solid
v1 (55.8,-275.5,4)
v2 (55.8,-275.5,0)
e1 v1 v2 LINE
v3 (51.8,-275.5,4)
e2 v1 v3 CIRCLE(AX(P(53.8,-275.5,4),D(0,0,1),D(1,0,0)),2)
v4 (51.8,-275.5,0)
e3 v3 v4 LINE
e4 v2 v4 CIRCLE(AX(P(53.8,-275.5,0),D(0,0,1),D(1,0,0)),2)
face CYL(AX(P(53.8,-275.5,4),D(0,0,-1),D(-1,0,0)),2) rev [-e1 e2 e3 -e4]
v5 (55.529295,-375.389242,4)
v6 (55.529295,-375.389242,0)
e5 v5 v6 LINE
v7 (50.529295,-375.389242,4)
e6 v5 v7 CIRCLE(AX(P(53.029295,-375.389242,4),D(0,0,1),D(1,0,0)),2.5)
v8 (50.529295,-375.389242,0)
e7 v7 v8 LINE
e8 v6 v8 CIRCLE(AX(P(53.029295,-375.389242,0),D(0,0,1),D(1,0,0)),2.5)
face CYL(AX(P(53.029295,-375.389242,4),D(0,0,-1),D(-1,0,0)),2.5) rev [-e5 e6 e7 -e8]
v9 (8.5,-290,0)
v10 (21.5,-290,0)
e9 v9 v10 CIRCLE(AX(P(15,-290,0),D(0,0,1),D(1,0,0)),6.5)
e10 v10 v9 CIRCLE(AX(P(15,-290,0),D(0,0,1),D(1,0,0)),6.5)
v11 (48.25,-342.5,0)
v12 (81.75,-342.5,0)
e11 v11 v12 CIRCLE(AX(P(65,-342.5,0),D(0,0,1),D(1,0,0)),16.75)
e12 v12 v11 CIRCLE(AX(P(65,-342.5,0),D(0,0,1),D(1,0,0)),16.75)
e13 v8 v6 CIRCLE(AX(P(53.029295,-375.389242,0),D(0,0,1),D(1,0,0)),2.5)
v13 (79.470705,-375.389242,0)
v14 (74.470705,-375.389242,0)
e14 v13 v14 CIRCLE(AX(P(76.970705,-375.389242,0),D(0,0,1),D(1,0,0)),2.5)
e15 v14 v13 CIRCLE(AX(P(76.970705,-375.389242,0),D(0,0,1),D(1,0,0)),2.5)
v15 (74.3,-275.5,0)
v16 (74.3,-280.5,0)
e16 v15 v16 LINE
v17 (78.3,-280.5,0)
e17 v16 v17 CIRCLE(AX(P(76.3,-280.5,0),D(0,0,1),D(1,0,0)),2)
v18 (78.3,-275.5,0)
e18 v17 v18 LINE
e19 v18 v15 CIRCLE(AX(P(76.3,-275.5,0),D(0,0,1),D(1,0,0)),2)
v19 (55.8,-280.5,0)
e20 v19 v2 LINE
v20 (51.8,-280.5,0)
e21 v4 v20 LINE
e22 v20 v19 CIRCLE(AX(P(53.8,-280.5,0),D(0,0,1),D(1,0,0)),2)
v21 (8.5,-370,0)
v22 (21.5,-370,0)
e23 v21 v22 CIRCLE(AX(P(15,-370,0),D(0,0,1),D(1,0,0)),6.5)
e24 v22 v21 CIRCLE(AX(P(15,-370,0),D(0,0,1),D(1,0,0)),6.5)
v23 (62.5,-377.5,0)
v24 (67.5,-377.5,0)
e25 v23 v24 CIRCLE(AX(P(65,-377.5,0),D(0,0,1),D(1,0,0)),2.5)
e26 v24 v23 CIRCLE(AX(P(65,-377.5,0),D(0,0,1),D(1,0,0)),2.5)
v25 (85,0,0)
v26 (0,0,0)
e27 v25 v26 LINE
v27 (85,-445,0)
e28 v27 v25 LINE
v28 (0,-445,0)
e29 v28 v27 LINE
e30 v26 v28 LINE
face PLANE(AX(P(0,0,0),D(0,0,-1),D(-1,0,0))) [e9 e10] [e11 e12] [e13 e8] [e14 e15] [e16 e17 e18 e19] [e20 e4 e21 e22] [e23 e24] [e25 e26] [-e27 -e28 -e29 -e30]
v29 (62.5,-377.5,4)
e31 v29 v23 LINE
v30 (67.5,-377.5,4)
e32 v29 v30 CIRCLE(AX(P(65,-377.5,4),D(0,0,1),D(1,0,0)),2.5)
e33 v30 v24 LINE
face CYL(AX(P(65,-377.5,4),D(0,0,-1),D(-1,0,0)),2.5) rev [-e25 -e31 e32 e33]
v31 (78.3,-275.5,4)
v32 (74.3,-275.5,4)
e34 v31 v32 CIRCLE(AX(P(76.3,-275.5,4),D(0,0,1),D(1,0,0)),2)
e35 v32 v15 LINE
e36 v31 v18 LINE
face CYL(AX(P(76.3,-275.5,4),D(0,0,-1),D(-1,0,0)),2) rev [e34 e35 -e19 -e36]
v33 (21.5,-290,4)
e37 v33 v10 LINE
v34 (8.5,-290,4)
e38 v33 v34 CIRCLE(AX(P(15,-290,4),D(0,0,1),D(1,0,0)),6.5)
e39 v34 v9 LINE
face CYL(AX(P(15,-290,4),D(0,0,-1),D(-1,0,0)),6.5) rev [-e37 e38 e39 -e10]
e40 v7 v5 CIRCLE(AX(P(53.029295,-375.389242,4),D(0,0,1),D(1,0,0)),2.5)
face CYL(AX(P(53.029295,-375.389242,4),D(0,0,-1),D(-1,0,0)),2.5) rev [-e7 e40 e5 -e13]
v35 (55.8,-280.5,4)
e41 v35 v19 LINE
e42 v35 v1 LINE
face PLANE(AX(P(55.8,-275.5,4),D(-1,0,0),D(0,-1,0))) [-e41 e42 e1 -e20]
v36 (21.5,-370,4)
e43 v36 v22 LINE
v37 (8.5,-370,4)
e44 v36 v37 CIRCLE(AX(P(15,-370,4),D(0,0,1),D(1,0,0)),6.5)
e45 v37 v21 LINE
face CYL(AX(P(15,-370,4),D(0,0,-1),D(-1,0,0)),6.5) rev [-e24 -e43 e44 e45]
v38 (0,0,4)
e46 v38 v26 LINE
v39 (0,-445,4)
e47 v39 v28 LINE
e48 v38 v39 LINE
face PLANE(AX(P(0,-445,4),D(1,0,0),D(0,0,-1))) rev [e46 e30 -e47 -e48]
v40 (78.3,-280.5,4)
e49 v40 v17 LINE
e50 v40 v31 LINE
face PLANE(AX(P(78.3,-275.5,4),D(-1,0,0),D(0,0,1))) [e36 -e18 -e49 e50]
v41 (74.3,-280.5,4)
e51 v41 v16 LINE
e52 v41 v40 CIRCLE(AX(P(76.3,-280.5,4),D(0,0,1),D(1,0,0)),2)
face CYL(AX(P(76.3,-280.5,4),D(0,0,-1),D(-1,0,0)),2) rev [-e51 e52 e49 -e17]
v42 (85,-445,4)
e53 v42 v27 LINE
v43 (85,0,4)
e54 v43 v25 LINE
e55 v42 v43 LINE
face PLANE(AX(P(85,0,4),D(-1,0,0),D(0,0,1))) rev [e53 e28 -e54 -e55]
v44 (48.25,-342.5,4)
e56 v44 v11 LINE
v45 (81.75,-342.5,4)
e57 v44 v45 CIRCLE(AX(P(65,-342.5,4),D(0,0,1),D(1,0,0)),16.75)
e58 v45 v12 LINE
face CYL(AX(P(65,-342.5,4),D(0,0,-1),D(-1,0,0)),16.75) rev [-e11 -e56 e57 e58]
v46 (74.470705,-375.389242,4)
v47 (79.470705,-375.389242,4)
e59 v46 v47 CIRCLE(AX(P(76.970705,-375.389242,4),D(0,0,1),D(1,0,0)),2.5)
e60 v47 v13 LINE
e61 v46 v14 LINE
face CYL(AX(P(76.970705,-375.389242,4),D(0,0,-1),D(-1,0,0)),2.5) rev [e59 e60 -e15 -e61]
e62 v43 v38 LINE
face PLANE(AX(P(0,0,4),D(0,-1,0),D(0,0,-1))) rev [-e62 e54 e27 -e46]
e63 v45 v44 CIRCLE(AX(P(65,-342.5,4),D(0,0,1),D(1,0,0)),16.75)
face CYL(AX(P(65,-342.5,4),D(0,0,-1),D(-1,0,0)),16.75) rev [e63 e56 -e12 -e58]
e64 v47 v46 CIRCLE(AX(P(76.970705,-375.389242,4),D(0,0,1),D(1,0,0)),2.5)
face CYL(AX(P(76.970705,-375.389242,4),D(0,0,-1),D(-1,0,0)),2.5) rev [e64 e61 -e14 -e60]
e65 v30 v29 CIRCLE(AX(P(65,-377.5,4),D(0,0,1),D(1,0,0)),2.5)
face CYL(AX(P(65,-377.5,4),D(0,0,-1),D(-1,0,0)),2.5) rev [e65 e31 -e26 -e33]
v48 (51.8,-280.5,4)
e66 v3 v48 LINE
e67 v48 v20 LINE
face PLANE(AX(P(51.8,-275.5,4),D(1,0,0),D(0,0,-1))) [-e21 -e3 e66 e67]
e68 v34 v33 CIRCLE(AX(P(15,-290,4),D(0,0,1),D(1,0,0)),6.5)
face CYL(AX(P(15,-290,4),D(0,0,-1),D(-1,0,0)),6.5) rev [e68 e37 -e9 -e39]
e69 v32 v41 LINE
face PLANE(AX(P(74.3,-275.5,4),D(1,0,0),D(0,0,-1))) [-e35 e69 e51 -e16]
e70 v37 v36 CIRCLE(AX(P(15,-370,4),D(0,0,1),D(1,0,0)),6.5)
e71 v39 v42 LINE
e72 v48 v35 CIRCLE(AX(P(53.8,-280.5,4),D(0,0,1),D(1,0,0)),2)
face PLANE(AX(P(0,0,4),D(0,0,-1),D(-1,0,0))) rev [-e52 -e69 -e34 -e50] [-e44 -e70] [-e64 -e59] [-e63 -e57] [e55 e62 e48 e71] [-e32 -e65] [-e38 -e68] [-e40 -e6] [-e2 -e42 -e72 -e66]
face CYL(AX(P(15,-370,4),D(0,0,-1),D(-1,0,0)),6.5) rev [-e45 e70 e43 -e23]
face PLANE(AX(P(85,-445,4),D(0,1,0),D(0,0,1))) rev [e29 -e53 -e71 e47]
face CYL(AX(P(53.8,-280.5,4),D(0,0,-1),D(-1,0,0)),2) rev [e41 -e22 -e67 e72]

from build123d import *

# Parameters (mm, degrees)
SKETCH_1_W      = 85
SKETCH_1_H      = 445
SKETCH_1_R      = 6.5
SKETCH_1_R_2    = 2.5
SKETCH_1_R_3    = 16.75
EXTRUDE_2_DEPTH = 4


with BuildPart() as part:
    # 草图1 → 凸台-拉伸2 (new body)
    with BuildSketch(Plane.XY):
        with Locations((42.5, -222.5)):
            Rectangle(SKETCH_1_W, SKETCH_1_H)
        with Locations((15, -370)):
            Circle(SKETCH_1_R, mode=Mode.SUBTRACT)
        with Locations((76.970705016, -375.389241728)):
            Circle(SKETCH_1_R_2, mode=Mode.SUBTRACT)
        with Locations((65, -377.5)):
            Circle(SKETCH_1_R_2, mode=Mode.SUBTRACT)
        with Locations((15, -290)):
            Circle(SKETCH_1_R, mode=Mode.SUBTRACT)
        with Locations((53.029294983, -375.389241728)):
            Circle(SKETCH_1_R_2, mode=Mode.SUBTRACT)
        with Locations((65, -342.5)):
            Circle(SKETCH_1_R_3, mode=Mode.SUBTRACT)
        with BuildLine():
            Line((78.3, -275.5), (78.3, -280.5))
            ThreePointArc((78.3, -280.5), (76.3, -282.5), (74.3, -280.5))
            Line((74.3, -280.5), (74.3, -275.5))
            ThreePointArc((74.3, -275.5), (76.3, -273.5), (78.3, -275.5))
        make_face(mode=Mode.SUBTRACT)
        with BuildLine():
            Line((55.8, -275.5), (55.8, -280.5))
            ThreePointArc((55.8, -280.5), (53.8, -282.5), (51.8, -280.5))
            Line((51.8, -280.5), (51.8, -275.5))
            ThreePointArc((51.8, -275.5), (53.8, -273.5), (55.8, -275.5))
        make_face(mode=Mode.SUBTRACT)
    extrude(amount=EXTRUDE_2_DEPTH)


solid = part.part
